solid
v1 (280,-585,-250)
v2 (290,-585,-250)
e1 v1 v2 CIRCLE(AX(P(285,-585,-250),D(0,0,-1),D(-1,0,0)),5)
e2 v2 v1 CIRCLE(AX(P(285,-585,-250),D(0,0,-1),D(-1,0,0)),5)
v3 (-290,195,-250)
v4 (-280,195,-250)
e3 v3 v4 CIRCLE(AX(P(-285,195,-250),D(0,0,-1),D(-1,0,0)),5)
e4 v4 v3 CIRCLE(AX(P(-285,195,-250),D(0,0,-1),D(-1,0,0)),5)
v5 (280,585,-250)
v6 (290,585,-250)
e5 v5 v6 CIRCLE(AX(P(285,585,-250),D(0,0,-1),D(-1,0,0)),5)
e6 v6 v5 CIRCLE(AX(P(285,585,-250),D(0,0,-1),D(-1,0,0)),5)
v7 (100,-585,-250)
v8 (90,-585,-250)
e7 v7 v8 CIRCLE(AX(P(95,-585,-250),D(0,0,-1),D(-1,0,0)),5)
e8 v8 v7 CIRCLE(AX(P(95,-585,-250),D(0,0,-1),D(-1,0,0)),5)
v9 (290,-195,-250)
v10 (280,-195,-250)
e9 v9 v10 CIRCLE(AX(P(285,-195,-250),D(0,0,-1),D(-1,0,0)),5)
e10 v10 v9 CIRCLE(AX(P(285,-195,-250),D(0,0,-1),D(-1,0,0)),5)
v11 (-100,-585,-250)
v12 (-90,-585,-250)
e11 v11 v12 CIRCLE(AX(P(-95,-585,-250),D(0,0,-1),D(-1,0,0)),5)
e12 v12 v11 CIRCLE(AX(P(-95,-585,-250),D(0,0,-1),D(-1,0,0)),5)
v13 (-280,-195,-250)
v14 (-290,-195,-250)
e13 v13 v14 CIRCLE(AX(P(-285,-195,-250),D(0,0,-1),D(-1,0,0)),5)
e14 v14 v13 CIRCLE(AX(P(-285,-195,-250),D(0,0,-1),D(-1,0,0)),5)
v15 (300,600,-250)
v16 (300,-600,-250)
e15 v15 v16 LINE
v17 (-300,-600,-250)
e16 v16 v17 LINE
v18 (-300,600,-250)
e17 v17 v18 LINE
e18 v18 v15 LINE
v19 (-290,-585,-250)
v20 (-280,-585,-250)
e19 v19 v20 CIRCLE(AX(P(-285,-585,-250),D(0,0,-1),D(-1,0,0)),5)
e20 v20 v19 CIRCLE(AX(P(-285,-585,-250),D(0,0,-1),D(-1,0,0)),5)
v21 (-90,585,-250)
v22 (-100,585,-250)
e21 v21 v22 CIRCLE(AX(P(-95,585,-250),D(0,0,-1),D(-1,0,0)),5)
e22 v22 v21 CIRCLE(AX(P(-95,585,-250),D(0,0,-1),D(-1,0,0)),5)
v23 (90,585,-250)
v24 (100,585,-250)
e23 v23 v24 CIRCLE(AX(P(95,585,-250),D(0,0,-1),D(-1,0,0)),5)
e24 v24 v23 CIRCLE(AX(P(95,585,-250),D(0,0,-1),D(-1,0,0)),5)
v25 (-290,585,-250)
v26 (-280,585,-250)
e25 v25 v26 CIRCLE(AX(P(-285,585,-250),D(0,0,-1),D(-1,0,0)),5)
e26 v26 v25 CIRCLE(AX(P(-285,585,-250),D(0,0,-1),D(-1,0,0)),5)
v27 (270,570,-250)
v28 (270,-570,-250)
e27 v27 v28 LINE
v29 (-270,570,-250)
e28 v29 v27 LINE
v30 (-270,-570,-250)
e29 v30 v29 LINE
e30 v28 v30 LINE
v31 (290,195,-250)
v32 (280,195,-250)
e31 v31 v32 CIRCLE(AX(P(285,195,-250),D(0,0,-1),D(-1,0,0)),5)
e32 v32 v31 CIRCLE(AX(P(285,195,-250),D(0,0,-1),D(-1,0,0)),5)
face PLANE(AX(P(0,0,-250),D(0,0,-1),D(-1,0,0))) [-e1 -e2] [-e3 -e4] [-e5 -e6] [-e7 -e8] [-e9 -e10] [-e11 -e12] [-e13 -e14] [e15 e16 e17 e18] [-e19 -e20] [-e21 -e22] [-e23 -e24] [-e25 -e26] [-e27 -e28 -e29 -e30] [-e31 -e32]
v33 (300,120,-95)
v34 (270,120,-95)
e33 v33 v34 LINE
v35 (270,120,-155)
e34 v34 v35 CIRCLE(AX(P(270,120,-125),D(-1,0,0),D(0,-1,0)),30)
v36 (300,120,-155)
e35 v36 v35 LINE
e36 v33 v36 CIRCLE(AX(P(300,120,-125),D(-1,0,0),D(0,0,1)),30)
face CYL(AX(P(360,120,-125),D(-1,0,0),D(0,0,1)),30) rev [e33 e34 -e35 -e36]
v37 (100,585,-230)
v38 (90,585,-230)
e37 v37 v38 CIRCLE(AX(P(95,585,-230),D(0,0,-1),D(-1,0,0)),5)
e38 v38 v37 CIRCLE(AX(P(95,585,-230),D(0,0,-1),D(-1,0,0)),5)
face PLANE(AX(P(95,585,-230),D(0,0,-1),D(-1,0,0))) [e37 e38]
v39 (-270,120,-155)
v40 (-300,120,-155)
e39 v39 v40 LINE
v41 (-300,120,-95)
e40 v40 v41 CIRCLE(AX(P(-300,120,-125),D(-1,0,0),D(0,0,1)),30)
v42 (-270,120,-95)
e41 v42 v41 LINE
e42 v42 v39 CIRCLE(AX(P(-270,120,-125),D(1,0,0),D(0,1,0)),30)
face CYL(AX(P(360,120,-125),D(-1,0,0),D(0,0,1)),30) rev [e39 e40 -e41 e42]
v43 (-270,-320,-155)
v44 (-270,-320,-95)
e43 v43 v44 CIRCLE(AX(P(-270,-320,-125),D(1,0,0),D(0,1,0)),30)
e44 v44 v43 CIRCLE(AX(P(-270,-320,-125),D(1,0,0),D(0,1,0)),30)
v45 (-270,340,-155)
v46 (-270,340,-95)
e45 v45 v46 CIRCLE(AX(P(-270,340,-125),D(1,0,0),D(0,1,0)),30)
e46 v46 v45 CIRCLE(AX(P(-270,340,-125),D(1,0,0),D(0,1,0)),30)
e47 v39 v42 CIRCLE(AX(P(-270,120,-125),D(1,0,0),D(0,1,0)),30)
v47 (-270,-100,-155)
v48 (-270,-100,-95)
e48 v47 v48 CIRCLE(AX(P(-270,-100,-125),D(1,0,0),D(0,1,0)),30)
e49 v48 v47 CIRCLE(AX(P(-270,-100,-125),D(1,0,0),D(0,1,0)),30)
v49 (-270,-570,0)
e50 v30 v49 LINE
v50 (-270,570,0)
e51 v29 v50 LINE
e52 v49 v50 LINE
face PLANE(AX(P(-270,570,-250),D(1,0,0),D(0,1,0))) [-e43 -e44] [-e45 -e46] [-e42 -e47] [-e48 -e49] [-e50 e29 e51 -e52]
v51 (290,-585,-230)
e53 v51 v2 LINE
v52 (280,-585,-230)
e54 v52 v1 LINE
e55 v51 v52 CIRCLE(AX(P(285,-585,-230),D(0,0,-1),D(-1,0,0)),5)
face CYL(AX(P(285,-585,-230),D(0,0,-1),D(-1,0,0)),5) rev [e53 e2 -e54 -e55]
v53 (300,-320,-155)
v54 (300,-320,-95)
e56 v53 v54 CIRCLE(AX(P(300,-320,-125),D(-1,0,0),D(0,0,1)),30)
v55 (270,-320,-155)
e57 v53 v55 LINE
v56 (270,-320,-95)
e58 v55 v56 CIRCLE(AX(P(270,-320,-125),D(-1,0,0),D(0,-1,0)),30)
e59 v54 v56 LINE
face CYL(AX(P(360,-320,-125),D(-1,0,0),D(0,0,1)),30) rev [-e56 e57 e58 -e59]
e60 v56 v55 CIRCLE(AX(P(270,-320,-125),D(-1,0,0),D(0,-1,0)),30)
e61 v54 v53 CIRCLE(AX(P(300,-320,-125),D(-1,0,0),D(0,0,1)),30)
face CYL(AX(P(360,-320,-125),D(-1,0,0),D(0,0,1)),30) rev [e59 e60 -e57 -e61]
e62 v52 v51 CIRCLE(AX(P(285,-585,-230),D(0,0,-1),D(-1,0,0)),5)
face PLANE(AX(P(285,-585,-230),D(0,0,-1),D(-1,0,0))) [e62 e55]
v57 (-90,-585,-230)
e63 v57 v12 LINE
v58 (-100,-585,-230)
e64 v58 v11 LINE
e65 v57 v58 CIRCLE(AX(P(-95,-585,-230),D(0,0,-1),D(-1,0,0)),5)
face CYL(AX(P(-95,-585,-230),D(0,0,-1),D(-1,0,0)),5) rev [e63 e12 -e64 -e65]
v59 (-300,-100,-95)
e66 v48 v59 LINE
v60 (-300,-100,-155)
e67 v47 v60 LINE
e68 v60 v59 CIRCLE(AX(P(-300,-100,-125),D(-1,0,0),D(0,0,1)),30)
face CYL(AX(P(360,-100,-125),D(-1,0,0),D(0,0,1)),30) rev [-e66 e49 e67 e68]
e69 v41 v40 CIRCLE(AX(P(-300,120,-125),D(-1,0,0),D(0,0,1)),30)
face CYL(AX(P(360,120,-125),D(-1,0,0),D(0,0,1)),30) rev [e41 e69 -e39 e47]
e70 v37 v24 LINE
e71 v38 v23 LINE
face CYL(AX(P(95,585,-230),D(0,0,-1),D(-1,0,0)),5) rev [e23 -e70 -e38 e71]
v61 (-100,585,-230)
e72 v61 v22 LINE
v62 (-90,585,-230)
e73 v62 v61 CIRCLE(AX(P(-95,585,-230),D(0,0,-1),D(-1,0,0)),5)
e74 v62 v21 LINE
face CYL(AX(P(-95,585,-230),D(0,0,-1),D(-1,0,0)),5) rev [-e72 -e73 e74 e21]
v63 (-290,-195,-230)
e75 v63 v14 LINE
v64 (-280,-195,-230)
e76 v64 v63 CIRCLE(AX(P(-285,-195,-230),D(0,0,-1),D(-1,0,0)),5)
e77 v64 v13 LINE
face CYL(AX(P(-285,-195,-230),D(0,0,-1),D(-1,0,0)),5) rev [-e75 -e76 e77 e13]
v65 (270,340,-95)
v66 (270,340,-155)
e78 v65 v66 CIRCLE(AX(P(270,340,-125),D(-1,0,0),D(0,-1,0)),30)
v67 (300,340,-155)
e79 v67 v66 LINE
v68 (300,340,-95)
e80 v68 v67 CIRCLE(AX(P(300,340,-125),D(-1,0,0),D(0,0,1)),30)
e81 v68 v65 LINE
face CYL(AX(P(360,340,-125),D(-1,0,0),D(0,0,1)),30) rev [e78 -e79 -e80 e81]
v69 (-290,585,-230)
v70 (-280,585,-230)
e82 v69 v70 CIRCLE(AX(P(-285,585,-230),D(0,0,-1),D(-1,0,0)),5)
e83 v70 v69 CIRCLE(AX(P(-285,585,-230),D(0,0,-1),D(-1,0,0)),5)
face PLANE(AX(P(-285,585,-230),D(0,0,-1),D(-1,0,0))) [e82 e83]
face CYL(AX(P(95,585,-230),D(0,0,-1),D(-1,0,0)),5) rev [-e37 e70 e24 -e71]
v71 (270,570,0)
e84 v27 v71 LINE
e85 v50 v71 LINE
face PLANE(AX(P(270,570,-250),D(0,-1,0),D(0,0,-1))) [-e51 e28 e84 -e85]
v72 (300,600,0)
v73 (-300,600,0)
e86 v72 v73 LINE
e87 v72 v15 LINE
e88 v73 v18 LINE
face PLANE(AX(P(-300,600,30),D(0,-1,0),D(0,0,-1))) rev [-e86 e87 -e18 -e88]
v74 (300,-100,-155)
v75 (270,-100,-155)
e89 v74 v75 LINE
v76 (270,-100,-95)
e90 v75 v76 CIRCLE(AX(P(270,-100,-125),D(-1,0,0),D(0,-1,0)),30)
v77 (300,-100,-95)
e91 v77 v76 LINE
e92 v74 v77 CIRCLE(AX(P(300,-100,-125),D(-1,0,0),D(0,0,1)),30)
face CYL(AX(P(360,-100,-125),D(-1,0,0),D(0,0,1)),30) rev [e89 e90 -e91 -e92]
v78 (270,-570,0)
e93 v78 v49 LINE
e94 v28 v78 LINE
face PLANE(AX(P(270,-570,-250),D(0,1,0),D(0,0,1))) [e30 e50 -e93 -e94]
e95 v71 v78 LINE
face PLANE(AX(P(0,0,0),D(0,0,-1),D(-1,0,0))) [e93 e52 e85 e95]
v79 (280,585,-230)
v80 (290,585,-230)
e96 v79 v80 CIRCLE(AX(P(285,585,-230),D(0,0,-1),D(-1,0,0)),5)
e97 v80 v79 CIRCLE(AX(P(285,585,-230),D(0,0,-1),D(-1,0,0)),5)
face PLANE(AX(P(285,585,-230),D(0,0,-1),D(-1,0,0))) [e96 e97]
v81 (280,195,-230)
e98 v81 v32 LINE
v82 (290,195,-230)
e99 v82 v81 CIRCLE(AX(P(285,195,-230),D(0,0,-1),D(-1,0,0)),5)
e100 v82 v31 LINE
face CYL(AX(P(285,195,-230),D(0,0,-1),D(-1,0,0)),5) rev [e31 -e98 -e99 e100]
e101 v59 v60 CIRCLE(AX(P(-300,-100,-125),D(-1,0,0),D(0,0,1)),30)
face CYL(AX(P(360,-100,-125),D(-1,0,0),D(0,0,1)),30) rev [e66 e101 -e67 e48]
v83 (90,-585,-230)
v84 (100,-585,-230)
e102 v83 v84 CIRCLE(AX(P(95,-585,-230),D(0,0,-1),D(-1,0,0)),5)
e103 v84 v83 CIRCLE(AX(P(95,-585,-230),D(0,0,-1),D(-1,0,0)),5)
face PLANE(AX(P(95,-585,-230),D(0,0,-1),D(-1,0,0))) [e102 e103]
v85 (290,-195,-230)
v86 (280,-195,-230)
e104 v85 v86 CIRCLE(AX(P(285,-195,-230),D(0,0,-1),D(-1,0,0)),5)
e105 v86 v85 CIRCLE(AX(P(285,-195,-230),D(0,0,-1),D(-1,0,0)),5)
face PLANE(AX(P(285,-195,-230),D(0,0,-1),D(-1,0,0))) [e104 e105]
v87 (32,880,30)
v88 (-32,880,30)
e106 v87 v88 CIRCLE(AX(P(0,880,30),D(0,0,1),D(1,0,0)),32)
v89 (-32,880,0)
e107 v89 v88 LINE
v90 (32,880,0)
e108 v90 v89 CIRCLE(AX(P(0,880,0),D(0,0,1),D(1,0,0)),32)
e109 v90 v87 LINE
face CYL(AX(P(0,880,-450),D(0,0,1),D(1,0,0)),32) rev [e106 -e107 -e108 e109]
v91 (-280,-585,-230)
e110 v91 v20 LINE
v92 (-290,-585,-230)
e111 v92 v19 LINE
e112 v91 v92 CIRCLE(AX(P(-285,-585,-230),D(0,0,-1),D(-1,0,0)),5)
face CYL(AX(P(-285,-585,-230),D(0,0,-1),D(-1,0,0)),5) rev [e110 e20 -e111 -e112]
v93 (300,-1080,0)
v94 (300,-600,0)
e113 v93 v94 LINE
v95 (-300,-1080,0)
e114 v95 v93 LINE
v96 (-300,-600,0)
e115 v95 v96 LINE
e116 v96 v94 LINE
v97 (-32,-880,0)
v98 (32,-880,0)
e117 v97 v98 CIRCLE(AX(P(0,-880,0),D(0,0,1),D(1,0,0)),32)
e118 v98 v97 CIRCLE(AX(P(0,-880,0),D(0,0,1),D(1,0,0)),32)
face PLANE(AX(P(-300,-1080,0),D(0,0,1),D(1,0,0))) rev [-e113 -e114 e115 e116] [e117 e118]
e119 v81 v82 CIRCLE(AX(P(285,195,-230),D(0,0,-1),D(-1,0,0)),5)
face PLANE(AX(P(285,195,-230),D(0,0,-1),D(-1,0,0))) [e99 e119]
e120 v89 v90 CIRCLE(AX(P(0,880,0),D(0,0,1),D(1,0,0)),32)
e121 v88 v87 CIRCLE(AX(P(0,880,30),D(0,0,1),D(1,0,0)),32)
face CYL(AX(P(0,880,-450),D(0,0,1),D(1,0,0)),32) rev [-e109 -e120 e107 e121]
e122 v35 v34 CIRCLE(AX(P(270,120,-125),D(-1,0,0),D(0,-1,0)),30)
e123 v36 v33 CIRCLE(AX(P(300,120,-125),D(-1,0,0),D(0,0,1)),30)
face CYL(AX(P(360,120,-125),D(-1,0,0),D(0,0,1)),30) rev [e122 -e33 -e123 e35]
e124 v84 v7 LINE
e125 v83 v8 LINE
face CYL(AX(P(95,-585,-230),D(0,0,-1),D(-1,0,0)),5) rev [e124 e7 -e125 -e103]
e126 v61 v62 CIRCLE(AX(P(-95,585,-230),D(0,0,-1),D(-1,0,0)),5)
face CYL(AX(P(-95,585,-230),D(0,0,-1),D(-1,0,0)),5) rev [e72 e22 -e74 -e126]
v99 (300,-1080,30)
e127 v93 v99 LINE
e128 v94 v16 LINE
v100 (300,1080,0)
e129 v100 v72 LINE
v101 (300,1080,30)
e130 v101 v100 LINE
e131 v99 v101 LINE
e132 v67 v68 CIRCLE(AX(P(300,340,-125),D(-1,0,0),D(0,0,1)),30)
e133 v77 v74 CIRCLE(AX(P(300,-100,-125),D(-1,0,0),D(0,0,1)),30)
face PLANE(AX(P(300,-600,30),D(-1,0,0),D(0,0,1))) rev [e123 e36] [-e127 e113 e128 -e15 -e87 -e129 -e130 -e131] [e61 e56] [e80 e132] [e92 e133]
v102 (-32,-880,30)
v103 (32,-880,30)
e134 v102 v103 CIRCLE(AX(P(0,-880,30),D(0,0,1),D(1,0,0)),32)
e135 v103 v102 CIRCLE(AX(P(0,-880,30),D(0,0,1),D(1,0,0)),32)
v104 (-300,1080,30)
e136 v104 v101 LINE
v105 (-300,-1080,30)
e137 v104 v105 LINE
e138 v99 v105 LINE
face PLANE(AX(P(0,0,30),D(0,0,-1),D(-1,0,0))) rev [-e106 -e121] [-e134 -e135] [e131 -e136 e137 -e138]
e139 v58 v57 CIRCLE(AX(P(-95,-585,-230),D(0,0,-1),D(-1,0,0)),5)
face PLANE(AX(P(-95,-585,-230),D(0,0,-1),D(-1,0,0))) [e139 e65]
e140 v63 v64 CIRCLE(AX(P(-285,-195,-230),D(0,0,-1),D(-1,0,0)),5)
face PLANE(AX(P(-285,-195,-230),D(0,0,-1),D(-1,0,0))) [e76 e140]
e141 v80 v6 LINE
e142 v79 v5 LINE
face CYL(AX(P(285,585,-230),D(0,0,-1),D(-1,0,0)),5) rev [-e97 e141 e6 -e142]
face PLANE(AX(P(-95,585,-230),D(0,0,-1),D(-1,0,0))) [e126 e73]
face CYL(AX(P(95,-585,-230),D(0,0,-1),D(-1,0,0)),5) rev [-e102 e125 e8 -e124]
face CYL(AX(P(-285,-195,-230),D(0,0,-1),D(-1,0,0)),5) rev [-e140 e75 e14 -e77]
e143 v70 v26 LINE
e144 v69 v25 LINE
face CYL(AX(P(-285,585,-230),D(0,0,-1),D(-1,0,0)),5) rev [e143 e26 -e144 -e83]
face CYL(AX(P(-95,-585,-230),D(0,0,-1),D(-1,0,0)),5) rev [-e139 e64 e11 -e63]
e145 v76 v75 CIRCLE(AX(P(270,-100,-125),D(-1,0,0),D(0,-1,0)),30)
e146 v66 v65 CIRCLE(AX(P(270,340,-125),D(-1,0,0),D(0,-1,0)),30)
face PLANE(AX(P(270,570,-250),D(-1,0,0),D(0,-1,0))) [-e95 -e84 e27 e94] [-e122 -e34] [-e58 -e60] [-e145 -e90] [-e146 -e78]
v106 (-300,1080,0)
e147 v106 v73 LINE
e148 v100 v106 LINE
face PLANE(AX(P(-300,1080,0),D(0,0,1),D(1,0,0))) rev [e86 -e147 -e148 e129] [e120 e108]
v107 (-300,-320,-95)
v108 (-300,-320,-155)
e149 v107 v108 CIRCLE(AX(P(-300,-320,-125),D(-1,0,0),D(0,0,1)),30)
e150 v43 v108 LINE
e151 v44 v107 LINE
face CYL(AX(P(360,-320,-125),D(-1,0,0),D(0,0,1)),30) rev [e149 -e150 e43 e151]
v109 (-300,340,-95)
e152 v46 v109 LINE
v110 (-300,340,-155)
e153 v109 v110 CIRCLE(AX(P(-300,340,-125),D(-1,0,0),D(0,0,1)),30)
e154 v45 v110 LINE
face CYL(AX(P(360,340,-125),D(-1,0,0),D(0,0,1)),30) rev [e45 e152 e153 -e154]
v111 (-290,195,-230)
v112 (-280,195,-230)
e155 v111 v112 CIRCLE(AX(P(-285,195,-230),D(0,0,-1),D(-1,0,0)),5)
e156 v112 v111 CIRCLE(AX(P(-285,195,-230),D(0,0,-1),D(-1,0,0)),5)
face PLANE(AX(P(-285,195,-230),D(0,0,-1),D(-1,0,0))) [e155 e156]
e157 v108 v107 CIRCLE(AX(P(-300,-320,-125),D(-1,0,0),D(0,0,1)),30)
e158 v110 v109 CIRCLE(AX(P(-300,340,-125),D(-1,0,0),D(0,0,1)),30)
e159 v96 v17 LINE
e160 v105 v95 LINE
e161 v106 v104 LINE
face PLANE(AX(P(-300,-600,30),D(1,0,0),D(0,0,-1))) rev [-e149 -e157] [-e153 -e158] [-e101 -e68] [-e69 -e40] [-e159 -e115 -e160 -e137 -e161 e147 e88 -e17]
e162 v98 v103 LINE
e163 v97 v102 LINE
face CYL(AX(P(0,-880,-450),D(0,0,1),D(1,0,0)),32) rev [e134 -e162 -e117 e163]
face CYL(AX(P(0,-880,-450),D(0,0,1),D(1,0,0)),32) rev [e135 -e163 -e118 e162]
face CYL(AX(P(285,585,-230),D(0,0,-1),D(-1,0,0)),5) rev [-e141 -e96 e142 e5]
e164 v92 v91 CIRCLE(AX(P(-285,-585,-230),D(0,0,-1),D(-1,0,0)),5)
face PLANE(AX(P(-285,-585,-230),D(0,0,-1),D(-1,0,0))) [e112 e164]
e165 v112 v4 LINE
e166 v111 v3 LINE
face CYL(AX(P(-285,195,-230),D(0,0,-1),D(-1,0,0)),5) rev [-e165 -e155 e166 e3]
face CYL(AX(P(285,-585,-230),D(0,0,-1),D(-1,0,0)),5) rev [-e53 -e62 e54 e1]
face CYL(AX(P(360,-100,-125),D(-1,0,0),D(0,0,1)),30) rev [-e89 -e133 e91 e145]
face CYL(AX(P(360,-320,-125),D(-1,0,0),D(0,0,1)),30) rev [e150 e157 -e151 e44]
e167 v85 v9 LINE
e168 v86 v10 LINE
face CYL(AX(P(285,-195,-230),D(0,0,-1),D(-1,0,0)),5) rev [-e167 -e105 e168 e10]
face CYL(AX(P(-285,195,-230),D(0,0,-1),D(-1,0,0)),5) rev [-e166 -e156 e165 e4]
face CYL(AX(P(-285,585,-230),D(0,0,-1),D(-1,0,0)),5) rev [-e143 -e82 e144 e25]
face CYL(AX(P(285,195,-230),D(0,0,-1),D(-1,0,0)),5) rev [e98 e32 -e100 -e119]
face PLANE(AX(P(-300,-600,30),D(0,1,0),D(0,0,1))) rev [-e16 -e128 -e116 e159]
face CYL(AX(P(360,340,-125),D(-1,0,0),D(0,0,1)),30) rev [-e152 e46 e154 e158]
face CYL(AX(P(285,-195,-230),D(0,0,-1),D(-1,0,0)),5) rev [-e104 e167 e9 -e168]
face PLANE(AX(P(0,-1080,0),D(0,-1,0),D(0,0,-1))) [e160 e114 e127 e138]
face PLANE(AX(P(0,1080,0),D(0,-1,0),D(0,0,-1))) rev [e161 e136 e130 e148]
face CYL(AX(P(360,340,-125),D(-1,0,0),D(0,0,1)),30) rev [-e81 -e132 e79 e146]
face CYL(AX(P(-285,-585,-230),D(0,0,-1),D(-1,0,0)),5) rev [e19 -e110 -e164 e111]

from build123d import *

# Parameters (mm, degrees)
SKETCH1_W                 = 600
SKETCH1_H                 = 1200
BOSS_EXTRUDE1_DEPTH       = 30
SKETCH3_W                 = 600
SKETCH3_H                 = 1200
SKETCH3_W_2               = 540
SKETCH3_H_2               = 1140
BOSS_EXTRUDE2_DEPTH       = 250
SKETCH4_R                 = 30
CUT_EXTRUDE2_DEPTH        = 660
LPATTERN1_COUNT           = 4
LPATTERN1_PITCH           = 220
SKETCH5_R                 = 5
CUT_EXTRUDE3_DEPTH        = 20
LPATTERN2_COUNT           = 4
LPATTERN2_PITCH           = 190
LPATTERN3_COUNT           = 4
LPATTERN3_PITCH           = 390
LPATTERN4_COPY_1_SKETCH_R = 5
LPATTERN4_COPY_1_DEPTH    = 20
LPATTERN4_COPY_2_SKETCH_R = 5
LPATTERN4_COPY_2_DEPTH    = 20
LPATTERN4_COPY_3_SKETCH_R = 5
LPATTERN4_COPY_3_DEPTH    = 20
LPATTERN4_COPY_4_SKETCH_R = 5
LPATTERN4_COPY_4_DEPTH    = 20
LPATTERN5_COPY_1_SKETCH_R = 5
LPATTERN5_COPY_1_DEPTH    = 20
LPATTERN5_COPY_2_SKETCH_R = 5
LPATTERN5_COPY_2_DEPTH    = 20
LPATTERN5_COPY_3_SKETCH_R = 5
LPATTERN5_COPY_3_DEPTH    = 20
LPATTERN5_COPY_4_SKETCH_R = 5
LPATTERN5_COPY_4_DEPTH    = 20
SKETCH6_W                 = 600
SKETCH6_H                 = 30
BOSS_EXTRUDE3_DEPTH       = 480
SKETCH8_W                 = 600
SKETCH8_H                 = 30
BOSS_EXTRUDE4_DEPTH       = 480
SKETCH9_R                 = 32
CUT_EXTRUDE4_DEPTH        = 480


with BuildPart() as part:
    # Sketch1 → Boss-Extrude1 (new body)
    with BuildSketch(Plane.XY):
        Rectangle(SKETCH1_W, SKETCH1_H)
    extrude(amount=BOSS_EXTRUDE1_DEPTH)

    # Sketch3 → Boss-Extrude2 (add)
    with BuildSketch(Plane(origin=(0, 0, 0), x_dir=(-1, 0, 0), z_dir=(0, 0, -1))):
        Rectangle(SKETCH3_W, SKETCH3_H)
        Rectangle(SKETCH3_W_2, SKETCH3_H_2, mode=Mode.SUBTRACT)
    extrude(amount=BOSS_EXTRUDE2_DEPTH)

    # Sketch4 → Cut-Extrude2 (cut)
    with BuildSketch(Plane.ZY.offset(300)):
        with Locations((-125, 340)):
            Circle(SKETCH4_R)
    cut_extrude2 = extrude(amount=-CUT_EXTRUDE2_DEPTH, mode=Mode.SUBTRACT)

    # LPattern1: Cut-Extrude2 ×4
    with Locations(*[(0, -i * LPATTERN1_PITCH, 0) for i in range(1, LPATTERN1_COUNT)]):
        add(cut_extrude2, mode=Mode.SUBTRACT)

    # Sketch5 → Cut-Extrude3 (cut)
    with BuildSketch(Plane(origin=(0, 0, -250), x_dir=(-1, 0, 0), z_dir=(0, 0, -1))):
        with Locations((-285, 585)):
            Circle(SKETCH5_R)
    cut_extrude3 = extrude(amount=-CUT_EXTRUDE3_DEPTH, mode=Mode.SUBTRACT)

    # LPattern2: Cut-Extrude3 ×4
    with Locations(*[(-i * LPATTERN2_PITCH, 0, 0) for i in range(1, LPATTERN2_COUNT)]):
        add(cut_extrude3, mode=Mode.SUBTRACT)

    # LPattern3: Cut-Extrude3 ×4
    with Locations(*[(0, -i * LPATTERN3_PITCH, 0) for i in range(1, LPATTERN3_COUNT)]):
        add(cut_extrude3, mode=Mode.SUBTRACT)

    # LPattern4 copy 1 sketch → LPattern4 copy 1 (cut)
    with BuildSketch(Plane(origin=(-570, -390, -250), x_dir=(-1, 0, 0), z_dir=(0, 0, -1))):
        with Locations((-285, 585)):
            Circle(LPATTERN4_COPY_1_SKETCH_R)
    extrude(amount=-LPATTERN4_COPY_1_DEPTH, mode=Mode.SUBTRACT)

    # LPattern4 copy 2 sketch → LPattern4 copy 2 (cut)
    with BuildSketch(Plane(origin=(-570, -780, -250), x_dir=(-1, 0, 0), z_dir=(0, 0, -1))):
        with Locations((-285, 585)):
            Circle(LPATTERN4_COPY_2_SKETCH_R)
    extrude(amount=-LPATTERN4_COPY_2_DEPTH, mode=Mode.SUBTRACT)

    # LPattern4 copy 3 sketch → LPattern4 copy 3 (cut)
    with BuildSketch(Plane(origin=(-570, -1170, -250), x_dir=(-1, 0, 0), z_dir=(0, 0, -1))):
        with Locations((-285, 585)):
            Circle(LPATTERN4_COPY_3_SKETCH_R)
    extrude(amount=-LPATTERN4_COPY_3_DEPTH, mode=Mode.SUBTRACT)

    # LPattern4 copy 4 sketch → LPattern4 copy 4 (cut)
    with BuildSketch(Plane(origin=(-570, 0, -250), x_dir=(-1, 0, 0), z_dir=(0, 0, -1))):
        with Locations((-285, 585)):
            Circle(LPATTERN4_COPY_4_SKETCH_R)
    extrude(amount=-LPATTERN4_COPY_4_DEPTH, mode=Mode.SUBTRACT)

    # LPattern5 copy 1 sketch → LPattern5 copy 1 (cut)
    with BuildSketch(Plane(origin=(-190, -1170, -250), x_dir=(-1, 0, 0), z_dir=(0, 0, -1))):
        with Locations((-285, 585)):
            Circle(LPATTERN5_COPY_1_SKETCH_R)
    extrude(amount=-LPATTERN5_COPY_1_DEPTH, mode=Mode.SUBTRACT)

    # LPattern5 copy 2 sketch → LPattern5 copy 2 (cut)
    with BuildSketch(Plane(origin=(-380, -1170, -250), x_dir=(-1, 0, 0), z_dir=(0, 0, -1))):
        with Locations((-285, 585)):
            Circle(LPATTERN5_COPY_2_SKETCH_R)
    extrude(amount=-LPATTERN5_COPY_2_DEPTH, mode=Mode.SUBTRACT)

    # LPattern5 copy 3 sketch → LPattern5 copy 3 (cut)
    with BuildSketch(Plane(origin=(-570, -1170, -250), x_dir=(-1, 0, 0), z_dir=(0, 0, -1))):
        with Locations((-285, 585)):
            Circle(LPATTERN5_COPY_3_SKETCH_R)
    extrude(amount=-LPATTERN5_COPY_3_DEPTH, mode=Mode.SUBTRACT)

    # LPattern5 copy 4 sketch → LPattern5 copy 4 (cut)
    with BuildSketch(Plane(origin=(0, -1170, -250), x_dir=(-1, 0, 0), z_dir=(0, 0, -1))):
        with Locations((-285, 585)):
            Circle(LPATTERN5_COPY_4_SKETCH_R)
    extrude(amount=-LPATTERN5_COPY_4_DEPTH, mode=Mode.SUBTRACT)

    # Sketch6 → Boss-Extrude3 (add)
    with BuildSketch(Plane.XZ.offset(600)):
        with Locations((0, 15)):
            Rectangle(SKETCH6_W, SKETCH6_H)
    extrude(amount=BOSS_EXTRUDE3_DEPTH)

    # Sketch8 → Boss-Extrude4 (add)
    with BuildSketch(Plane(origin=(0, 600, 0), x_dir=(1, 0, 0), z_dir=(0, 1, 0))):
        with Locations((0, -15)):
            Rectangle(SKETCH8_W, SKETCH8_H)
    extrude(amount=BOSS_EXTRUDE4_DEPTH)

    # Sketch9 → Cut-Extrude4 (cut)
    with BuildSketch(Plane.XY.offset(30)):
        with Locations((0, 880)):
            Circle(SKETCH9_R)
        with Locations((0, -880)):
            Circle(SKETCH9_R)
    extrude(amount=-CUT_EXTRUDE4_DEPTH, mode=Mode.SUBTRACT)


solid = part.part
